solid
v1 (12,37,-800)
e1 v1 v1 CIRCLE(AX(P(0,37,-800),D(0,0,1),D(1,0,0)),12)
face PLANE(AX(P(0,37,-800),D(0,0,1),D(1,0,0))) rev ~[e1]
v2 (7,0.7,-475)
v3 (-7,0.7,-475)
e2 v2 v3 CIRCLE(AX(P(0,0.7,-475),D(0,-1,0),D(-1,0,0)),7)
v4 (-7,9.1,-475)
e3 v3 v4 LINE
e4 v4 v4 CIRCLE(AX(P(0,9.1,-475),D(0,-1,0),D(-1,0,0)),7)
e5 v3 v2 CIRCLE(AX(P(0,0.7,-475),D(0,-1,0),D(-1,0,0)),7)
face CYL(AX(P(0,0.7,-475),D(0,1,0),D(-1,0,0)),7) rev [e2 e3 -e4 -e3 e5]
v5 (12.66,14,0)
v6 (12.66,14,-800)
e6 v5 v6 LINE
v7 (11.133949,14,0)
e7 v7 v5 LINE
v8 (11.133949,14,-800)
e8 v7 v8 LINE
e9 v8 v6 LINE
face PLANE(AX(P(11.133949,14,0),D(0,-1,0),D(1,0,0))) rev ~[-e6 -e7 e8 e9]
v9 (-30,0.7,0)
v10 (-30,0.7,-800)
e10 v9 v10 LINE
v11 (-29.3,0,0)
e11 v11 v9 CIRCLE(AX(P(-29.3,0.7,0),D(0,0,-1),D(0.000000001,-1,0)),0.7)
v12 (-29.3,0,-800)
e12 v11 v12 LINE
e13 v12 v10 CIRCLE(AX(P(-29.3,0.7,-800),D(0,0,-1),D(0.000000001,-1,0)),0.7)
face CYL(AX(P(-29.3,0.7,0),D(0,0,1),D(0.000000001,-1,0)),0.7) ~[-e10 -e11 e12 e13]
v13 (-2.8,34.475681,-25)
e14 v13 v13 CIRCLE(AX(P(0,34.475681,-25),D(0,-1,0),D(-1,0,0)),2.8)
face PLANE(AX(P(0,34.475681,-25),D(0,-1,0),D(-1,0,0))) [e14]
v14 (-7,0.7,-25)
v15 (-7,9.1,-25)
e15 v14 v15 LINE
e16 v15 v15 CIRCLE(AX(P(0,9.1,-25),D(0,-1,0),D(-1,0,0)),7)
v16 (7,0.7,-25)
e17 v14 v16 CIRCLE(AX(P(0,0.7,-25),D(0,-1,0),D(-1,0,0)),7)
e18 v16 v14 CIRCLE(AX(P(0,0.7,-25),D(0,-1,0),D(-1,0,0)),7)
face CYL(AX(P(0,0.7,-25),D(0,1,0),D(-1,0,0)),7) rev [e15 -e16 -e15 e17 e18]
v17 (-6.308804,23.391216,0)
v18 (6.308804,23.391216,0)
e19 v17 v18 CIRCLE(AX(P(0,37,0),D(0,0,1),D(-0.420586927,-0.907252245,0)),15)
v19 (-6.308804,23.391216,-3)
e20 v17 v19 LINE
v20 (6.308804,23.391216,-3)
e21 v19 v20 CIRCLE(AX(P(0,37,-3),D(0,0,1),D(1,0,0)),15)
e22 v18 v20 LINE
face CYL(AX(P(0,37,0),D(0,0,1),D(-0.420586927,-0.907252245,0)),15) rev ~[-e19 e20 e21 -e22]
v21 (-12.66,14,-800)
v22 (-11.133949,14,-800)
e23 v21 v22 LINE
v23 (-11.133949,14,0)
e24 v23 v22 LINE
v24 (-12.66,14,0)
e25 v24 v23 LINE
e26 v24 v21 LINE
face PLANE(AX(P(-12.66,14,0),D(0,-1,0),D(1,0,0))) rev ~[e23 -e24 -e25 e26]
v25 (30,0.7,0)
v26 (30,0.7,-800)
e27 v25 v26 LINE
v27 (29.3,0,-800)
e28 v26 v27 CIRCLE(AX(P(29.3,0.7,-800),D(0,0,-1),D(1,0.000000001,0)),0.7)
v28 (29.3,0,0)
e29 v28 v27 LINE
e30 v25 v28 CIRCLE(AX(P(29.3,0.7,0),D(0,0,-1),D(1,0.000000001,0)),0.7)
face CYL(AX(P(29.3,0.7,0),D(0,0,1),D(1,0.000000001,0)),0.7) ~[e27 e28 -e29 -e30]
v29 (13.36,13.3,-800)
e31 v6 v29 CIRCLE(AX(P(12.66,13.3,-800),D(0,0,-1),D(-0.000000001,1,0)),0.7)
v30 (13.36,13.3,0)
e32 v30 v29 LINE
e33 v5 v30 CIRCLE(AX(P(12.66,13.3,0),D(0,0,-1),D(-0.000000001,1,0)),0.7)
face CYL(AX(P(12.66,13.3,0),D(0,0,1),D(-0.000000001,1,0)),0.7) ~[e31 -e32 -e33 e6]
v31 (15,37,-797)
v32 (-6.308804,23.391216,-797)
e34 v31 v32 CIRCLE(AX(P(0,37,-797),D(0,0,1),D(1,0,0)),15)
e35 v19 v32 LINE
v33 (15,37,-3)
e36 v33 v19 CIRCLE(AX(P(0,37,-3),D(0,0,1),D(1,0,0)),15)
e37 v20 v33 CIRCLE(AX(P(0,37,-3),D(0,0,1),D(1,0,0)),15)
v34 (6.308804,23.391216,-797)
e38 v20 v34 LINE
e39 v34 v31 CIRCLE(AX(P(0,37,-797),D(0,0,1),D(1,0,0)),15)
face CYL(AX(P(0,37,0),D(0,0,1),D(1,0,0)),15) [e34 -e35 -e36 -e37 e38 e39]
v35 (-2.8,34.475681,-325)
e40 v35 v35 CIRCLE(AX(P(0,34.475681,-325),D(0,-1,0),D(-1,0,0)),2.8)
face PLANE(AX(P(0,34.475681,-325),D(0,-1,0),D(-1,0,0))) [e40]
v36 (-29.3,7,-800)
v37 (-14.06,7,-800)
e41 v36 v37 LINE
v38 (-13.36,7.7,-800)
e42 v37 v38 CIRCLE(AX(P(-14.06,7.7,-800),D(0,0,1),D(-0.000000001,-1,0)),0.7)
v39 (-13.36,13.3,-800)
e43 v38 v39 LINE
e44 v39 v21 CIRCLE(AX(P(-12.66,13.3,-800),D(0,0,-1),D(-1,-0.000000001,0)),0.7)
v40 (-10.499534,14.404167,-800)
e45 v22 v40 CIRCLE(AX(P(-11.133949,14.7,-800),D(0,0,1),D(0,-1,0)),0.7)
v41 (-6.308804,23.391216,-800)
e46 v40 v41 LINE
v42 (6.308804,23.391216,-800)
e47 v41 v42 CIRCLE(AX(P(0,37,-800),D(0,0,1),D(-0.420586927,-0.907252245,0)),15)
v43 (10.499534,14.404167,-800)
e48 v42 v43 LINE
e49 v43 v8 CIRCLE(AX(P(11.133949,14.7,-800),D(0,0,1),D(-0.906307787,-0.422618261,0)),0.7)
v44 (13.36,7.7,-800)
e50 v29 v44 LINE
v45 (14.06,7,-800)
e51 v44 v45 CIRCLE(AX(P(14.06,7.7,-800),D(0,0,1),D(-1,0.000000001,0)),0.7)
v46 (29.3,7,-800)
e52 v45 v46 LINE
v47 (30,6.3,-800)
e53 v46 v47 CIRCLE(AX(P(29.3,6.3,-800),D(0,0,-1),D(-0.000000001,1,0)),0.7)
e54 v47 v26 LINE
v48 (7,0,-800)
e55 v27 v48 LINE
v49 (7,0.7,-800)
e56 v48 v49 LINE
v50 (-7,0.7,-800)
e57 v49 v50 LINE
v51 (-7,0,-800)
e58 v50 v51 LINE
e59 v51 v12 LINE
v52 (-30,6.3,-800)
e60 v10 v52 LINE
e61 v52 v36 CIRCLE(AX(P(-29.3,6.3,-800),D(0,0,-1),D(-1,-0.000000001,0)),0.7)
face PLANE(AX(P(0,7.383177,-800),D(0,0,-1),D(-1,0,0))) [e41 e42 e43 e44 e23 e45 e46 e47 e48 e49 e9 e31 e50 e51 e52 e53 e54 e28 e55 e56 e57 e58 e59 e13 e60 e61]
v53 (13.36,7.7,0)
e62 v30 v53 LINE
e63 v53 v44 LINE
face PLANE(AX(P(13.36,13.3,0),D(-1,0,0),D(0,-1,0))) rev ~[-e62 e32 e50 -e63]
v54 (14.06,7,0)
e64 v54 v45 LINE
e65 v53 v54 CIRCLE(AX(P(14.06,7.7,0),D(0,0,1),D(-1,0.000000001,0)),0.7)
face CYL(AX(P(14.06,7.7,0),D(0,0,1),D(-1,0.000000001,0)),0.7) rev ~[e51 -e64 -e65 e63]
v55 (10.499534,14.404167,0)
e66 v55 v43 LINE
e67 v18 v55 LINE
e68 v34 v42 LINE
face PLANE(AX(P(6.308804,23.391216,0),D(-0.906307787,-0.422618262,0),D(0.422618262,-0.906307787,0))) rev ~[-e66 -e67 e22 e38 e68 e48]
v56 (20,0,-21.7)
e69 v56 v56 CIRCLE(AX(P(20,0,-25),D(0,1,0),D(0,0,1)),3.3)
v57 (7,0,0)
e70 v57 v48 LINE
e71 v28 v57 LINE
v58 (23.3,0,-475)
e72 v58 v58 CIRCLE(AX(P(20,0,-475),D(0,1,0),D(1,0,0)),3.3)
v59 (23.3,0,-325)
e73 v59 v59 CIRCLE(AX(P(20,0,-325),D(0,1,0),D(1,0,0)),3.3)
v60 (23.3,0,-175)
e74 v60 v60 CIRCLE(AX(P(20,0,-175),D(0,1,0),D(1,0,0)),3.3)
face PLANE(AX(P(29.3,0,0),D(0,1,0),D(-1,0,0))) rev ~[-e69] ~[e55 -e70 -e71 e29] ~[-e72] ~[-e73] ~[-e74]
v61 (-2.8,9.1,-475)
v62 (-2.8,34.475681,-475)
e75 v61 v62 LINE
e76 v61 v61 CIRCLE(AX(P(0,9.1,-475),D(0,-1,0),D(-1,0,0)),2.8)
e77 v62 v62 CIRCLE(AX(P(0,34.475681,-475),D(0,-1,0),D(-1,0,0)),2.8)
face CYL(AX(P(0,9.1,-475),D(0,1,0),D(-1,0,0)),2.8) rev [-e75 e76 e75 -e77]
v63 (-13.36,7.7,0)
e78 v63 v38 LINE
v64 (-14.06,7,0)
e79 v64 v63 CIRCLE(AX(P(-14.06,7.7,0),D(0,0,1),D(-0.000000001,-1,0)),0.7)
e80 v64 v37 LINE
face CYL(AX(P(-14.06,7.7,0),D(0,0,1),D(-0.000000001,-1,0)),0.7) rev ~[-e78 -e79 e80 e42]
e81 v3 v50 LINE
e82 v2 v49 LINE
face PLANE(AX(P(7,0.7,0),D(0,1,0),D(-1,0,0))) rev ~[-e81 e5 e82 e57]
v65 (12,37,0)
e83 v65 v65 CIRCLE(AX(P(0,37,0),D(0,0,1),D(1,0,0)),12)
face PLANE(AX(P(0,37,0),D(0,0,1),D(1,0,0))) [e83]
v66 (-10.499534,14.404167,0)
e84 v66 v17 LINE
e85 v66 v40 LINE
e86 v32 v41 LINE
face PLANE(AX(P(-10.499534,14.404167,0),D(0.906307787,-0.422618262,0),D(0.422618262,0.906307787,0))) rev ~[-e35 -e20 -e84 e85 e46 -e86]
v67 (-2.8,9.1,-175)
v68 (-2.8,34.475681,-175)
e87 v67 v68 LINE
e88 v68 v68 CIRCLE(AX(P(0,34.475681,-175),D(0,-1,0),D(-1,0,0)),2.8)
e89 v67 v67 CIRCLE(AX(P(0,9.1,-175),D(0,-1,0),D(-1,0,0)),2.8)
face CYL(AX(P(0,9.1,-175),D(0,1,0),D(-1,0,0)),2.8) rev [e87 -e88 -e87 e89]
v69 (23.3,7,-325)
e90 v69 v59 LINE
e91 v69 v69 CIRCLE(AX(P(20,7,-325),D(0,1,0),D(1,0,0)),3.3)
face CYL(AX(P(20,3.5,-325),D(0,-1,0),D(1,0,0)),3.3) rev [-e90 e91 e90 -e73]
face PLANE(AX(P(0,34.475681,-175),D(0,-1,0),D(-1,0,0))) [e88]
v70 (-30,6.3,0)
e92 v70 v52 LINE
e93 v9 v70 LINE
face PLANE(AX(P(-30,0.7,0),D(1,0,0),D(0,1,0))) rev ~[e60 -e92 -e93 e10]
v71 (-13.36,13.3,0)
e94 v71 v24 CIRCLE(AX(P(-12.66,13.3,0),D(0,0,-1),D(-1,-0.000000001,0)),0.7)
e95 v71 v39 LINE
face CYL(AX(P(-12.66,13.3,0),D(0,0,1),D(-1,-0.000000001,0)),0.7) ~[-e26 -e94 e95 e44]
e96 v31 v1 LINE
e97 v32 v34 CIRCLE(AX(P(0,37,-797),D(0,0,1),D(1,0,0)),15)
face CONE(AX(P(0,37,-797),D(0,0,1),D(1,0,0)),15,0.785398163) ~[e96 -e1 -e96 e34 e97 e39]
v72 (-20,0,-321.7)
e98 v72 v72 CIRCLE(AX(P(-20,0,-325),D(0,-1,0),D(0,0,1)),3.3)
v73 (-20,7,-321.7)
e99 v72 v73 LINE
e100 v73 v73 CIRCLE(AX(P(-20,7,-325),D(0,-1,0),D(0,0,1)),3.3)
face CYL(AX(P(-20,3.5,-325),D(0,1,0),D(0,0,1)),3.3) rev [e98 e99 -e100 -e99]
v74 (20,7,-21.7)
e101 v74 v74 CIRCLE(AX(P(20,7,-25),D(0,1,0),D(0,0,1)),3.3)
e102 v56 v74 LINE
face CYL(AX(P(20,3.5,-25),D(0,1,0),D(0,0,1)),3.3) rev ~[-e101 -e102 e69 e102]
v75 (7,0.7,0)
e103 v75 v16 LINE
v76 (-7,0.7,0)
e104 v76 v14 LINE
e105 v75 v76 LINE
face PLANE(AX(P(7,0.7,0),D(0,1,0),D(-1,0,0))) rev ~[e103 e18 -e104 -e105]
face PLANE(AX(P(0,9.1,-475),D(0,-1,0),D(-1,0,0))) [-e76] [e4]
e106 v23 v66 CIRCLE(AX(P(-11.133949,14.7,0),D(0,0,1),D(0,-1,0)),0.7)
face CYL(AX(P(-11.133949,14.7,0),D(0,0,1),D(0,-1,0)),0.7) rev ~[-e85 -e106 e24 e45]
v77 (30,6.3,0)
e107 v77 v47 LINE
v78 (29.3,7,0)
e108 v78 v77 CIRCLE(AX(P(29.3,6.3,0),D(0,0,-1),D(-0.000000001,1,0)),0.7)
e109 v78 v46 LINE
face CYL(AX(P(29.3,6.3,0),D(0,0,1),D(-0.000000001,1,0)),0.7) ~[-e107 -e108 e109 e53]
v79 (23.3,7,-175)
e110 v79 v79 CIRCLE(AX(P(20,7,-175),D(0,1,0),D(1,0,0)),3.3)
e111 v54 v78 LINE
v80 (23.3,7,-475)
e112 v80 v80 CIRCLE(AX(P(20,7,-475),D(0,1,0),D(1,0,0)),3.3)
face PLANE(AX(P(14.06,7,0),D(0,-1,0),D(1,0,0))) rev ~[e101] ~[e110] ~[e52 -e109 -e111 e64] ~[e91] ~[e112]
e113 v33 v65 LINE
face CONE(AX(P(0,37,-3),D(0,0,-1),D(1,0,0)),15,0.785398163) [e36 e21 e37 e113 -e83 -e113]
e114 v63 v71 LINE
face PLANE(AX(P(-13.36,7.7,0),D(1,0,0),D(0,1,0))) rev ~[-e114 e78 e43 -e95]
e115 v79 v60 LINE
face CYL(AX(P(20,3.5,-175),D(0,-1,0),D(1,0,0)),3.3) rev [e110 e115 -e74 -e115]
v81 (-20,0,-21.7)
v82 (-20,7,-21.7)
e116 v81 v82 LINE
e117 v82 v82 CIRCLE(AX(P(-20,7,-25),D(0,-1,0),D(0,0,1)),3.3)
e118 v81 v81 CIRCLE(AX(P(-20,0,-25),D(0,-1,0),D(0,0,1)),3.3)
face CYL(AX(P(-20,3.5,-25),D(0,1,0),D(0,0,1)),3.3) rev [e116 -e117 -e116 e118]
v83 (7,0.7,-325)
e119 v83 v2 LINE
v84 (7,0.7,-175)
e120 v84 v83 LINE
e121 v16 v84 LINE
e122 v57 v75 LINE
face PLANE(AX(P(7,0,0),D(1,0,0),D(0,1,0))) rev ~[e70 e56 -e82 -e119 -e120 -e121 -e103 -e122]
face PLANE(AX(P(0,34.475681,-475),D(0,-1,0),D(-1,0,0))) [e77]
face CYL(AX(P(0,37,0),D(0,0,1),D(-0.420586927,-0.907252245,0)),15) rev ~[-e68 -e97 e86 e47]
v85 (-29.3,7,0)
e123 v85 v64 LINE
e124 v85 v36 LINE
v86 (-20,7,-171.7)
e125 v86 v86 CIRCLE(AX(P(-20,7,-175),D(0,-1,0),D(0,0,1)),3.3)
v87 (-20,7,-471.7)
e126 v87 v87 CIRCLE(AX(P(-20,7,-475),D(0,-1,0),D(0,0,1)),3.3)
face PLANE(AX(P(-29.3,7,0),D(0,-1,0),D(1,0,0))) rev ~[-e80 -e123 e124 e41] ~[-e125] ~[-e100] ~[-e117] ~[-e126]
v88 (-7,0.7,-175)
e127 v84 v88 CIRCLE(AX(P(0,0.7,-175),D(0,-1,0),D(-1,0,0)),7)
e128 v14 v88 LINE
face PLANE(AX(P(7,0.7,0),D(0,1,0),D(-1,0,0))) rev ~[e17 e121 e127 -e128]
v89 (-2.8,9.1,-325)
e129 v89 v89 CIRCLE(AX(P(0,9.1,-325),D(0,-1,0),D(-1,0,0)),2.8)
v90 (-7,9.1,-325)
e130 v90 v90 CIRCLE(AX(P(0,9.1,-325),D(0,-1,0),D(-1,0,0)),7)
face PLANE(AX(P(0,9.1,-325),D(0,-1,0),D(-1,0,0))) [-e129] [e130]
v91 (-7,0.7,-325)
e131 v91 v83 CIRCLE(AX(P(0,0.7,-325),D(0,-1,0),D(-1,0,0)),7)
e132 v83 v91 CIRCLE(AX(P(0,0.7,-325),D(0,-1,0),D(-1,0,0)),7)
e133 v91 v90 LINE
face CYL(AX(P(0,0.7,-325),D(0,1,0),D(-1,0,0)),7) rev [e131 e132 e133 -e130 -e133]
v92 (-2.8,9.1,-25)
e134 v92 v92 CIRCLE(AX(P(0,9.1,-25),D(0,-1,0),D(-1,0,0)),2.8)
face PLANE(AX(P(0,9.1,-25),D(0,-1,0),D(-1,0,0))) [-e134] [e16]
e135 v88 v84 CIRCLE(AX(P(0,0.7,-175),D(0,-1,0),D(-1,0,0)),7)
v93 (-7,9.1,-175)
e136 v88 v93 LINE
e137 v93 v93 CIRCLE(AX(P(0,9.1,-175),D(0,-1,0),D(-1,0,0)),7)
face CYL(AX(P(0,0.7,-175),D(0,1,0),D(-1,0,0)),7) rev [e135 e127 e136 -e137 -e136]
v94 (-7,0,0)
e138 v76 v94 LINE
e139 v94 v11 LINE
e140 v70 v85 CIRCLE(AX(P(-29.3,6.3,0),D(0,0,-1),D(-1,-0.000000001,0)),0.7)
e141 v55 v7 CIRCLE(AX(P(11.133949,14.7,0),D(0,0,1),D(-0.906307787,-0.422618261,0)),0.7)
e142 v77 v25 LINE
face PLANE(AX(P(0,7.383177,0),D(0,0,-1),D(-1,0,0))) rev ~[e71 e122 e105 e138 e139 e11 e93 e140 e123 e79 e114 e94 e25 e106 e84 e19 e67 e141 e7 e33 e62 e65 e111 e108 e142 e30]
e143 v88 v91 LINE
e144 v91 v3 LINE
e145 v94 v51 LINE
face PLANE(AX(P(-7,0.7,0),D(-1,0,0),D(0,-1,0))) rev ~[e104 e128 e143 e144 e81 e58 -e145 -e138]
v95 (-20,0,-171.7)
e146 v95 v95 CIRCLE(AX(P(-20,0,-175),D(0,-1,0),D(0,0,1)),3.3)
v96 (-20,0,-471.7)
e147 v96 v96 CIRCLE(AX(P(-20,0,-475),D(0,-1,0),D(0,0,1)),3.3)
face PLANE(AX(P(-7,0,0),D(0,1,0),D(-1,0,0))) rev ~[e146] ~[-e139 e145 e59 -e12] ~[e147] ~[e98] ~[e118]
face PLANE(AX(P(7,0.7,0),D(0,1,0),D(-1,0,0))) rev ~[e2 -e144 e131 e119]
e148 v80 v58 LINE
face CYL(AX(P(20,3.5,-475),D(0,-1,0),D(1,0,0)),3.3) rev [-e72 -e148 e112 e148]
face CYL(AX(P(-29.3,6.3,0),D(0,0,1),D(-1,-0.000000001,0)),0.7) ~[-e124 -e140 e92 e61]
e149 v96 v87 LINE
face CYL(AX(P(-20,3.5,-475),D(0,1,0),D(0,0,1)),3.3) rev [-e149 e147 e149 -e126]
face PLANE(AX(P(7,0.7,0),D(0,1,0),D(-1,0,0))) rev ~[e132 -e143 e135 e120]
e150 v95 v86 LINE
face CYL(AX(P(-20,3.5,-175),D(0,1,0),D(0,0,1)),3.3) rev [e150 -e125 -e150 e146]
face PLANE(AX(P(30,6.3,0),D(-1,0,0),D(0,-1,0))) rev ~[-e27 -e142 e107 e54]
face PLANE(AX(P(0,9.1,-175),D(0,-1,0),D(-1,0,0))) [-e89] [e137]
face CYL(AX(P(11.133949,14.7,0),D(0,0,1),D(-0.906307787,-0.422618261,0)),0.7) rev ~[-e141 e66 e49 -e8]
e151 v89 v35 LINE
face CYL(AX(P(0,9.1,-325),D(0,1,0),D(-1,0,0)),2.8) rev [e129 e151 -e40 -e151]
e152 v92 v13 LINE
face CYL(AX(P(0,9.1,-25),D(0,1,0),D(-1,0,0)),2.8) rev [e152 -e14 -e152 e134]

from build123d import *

# Parameters (mm, degrees)
SKETCH6_R                      = 15
BOSS_EXTRUDE2_DEPTH            = 800
CHAMFER1_SIZE                  = 3
BOSS_EXTRUDE1_DEPTH            = 800
SKETCH4_W                      = 3.3
SKETCH4_H                      = 7
CURVE_PATTERN1_COUNT           = 4
CURVE_PATTERN1_PITCH           = 150
CURVE_PATTERN1_COPY_1_SKETCH_W = 3.3
CURVE_PATTERN1_COPY_1_SKETCH_H = 7
CURVE_PATTERN1_COPY_2_SKETCH_W = 3.3
CURVE_PATTERN1_COPY_2_SKETCH_H = 7
CURVE_PATTERN1_COPY_3_SKETCH_W = 3.3
CURVE_PATTERN1_COPY_3_SKETCH_H = 7


with BuildPart() as part:
    # Sketch6 → Boss-Extrude2 (new body)
    with BuildSketch(Plane.XY):
        with Locations((0, 37)):
            Circle(SKETCH6_R)
    extrude(amount=-BOSS_EXTRUDE2_DEPTH)

    # Chamfer1
    chamfer1_edges = [part.edges().sort_by_distance(p)[0] for p in [
        (-15, 37, 0),
        (-15, 37, -800),
    ]]
    chamfer(chamfer1_edges, length=CHAMFER1_SIZE)

    # Sketch3 → Boss-Extrude1 (add)
    with BuildSketch(Plane.XY):
        with BuildLine():
            Line((-10.499533732, 14.404167217), (-6.30880391, 23.391216321))
            ThreePointArc((-6.30880391, 23.391216321), (0, 22), (6.30880391, 23.391216321))
            Line((6.30880391, 23.391216321), (10.499533732, 14.404167217))
            ThreePointArc((10.499533732, 14.404167217), (10.757839457, 14.109625988), (11.133949183, 14))
            Line((11.133949183, 14), (12.66, 14))
            ThreePointArc((12.66, 14), (13.154974747, 13.794974747), (13.36, 13.3))
            Line((13.36, 13.3), (13.36, 7.7))
            ThreePointArc((13.36, 7.7), (13.565025253, 7.205025253), (14.06, 7))
            Line((14.06, 7), (29.3, 7))
            ThreePointArc((29.3, 7), (29.794974747, 6.794974747), (30, 6.3))
            Line((30, 6.3), (30, 0.7))
            ThreePointArc((30, 0.7), (29.794974747, 0.205025253), (29.3, 0))
            Line((29.3, 0), (7, 0))
            Line((7, 0), (7, 0.7))
            Line((7, 0.7), (-7, 0.7))
            Line((-7, 0.7), (-7, 0))
            Line((-7, 0), (-29.3, 0))
            ThreePointArc((-29.3, 0), (-29.794974747, 0.205025253), (-30, 0.7))
            Line((-30, 0.7), (-30, 6.3))
            ThreePointArc((-30, 6.3), (-29.794974747, 6.794974747), (-29.3, 7))
            Line((-29.3, 7), (-14.06, 7))
            ThreePointArc((-14.06, 7), (-13.565025253, 7.205025253), (-13.36, 7.7))
            Line((-13.36, 7.7), (-13.36, 13.3))
            ThreePointArc((-13.36, 13.3), (-13.154974747, 13.794974747), (-12.66, 14))
            Line((-12.66, 14), (-11.133949183, 14))
            ThreePointArc((-11.133949183, 14), (-10.757839457, 14.109625988), (-10.499533732, 14.404167217))
        make_face()
    extrude(amount=-BOSS_EXTRUDE1_DEPTH)

    # Sketch4 → Cut-Revolve1 (revolve, cut)
    with BuildSketch(Plane.XY.offset(-25), mode=Mode.PRIVATE) as cut_revolve1_sk:
        with Locations((-21.65, 3.5)):
            Rectangle(SKETCH4_W, SKETCH4_H)
    cut_revolve1 = revolve(cut_revolve1_sk.sketch.rotate(Axis((-20, 7, -25), (0, -1, 0)), 270), axis=Axis((-20, 7, -25), (0, -1, 0)), mode=Mode.SUBTRACT)

    # Mirror1: Cut-Revolve1 across plane
    add(cut_revolve1.mirror(Plane(origin=(0, 0, 0), x_dir=(0, 0, 1), z_dir=(1, 0, 0))), mode=Mode.SUBTRACT)

    # Sketch5 → Cut-Revolve2 (revolve, cut)
    with BuildSketch(Plane.XY.offset(-25)):
        Polygon((-7, 0.7), (-7, 9.1), (-2.8, 9.1), (-2.8, 34.475681392), (0, 34.475681392), (0, 0.7), align=None)
    cut_revolve2 = revolve(axis=Axis((0, 34.475681392, -25), (0, -1, 0)), mode=Mode.SUBTRACT)

    # Curve Pattern1: Cut-Revolve1, Cut-Revolve2 ×4
    with Locations(*[(0, 0, -i * CURVE_PATTERN1_PITCH) for i in range(1, CURVE_PATTERN1_COUNT)]):
        add(cut_revolve1, mode=Mode.SUBTRACT)
        add(cut_revolve2, mode=Mode.SUBTRACT)

    # Curve Pattern1 copy 1 sketch → Curve Pattern1 copy 1 (revolve, cut)
    with BuildSketch(Plane(origin=(0, 0, -175), x_dir=(-1, 0, 0), z_dir=(0, 0, 1))):
        with Locations((-21.65, -3.5)):
            Rectangle(CURVE_PATTERN1_COPY_1_SKETCH_W, CURVE_PATTERN1_COPY_1_SKETCH_H)
    revolve(axis=Axis((20, 7, -175), (0, 1, 0)), mode=Mode.SUBTRACT)

    # Curve Pattern1 copy 2 sketch → Curve Pattern1 copy 2 (revolve, cut)
    with BuildSketch(Plane(origin=(0, 0, -325), x_dir=(-1, 0, 0), z_dir=(0, 0, 1))):
        with Locations((-21.65, -3.5)):
            Rectangle(CURVE_PATTERN1_COPY_2_SKETCH_W, CURVE_PATTERN1_COPY_2_SKETCH_H)
    revolve(axis=Axis((20, 7, -325), (0, 1, 0)), mode=Mode.SUBTRACT)

    # Curve Pattern1 copy 3 sketch → Curve Pattern1 copy 3 (revolve, cut)
    with BuildSketch(Plane(origin=(0, 0, -475), x_dir=(-1, 0, 0), z_dir=(0, 0, 1))):
        with Locations((-21.65, -3.5)):
            Rectangle(CURVE_PATTERN1_COPY_3_SKETCH_W, CURVE_PATTERN1_COPY_3_SKETCH_H)
    revolve(axis=Axis((20, 7, -475), (0, 1, 0)), mode=Mode.SUBTRACT)


solid = part.part
